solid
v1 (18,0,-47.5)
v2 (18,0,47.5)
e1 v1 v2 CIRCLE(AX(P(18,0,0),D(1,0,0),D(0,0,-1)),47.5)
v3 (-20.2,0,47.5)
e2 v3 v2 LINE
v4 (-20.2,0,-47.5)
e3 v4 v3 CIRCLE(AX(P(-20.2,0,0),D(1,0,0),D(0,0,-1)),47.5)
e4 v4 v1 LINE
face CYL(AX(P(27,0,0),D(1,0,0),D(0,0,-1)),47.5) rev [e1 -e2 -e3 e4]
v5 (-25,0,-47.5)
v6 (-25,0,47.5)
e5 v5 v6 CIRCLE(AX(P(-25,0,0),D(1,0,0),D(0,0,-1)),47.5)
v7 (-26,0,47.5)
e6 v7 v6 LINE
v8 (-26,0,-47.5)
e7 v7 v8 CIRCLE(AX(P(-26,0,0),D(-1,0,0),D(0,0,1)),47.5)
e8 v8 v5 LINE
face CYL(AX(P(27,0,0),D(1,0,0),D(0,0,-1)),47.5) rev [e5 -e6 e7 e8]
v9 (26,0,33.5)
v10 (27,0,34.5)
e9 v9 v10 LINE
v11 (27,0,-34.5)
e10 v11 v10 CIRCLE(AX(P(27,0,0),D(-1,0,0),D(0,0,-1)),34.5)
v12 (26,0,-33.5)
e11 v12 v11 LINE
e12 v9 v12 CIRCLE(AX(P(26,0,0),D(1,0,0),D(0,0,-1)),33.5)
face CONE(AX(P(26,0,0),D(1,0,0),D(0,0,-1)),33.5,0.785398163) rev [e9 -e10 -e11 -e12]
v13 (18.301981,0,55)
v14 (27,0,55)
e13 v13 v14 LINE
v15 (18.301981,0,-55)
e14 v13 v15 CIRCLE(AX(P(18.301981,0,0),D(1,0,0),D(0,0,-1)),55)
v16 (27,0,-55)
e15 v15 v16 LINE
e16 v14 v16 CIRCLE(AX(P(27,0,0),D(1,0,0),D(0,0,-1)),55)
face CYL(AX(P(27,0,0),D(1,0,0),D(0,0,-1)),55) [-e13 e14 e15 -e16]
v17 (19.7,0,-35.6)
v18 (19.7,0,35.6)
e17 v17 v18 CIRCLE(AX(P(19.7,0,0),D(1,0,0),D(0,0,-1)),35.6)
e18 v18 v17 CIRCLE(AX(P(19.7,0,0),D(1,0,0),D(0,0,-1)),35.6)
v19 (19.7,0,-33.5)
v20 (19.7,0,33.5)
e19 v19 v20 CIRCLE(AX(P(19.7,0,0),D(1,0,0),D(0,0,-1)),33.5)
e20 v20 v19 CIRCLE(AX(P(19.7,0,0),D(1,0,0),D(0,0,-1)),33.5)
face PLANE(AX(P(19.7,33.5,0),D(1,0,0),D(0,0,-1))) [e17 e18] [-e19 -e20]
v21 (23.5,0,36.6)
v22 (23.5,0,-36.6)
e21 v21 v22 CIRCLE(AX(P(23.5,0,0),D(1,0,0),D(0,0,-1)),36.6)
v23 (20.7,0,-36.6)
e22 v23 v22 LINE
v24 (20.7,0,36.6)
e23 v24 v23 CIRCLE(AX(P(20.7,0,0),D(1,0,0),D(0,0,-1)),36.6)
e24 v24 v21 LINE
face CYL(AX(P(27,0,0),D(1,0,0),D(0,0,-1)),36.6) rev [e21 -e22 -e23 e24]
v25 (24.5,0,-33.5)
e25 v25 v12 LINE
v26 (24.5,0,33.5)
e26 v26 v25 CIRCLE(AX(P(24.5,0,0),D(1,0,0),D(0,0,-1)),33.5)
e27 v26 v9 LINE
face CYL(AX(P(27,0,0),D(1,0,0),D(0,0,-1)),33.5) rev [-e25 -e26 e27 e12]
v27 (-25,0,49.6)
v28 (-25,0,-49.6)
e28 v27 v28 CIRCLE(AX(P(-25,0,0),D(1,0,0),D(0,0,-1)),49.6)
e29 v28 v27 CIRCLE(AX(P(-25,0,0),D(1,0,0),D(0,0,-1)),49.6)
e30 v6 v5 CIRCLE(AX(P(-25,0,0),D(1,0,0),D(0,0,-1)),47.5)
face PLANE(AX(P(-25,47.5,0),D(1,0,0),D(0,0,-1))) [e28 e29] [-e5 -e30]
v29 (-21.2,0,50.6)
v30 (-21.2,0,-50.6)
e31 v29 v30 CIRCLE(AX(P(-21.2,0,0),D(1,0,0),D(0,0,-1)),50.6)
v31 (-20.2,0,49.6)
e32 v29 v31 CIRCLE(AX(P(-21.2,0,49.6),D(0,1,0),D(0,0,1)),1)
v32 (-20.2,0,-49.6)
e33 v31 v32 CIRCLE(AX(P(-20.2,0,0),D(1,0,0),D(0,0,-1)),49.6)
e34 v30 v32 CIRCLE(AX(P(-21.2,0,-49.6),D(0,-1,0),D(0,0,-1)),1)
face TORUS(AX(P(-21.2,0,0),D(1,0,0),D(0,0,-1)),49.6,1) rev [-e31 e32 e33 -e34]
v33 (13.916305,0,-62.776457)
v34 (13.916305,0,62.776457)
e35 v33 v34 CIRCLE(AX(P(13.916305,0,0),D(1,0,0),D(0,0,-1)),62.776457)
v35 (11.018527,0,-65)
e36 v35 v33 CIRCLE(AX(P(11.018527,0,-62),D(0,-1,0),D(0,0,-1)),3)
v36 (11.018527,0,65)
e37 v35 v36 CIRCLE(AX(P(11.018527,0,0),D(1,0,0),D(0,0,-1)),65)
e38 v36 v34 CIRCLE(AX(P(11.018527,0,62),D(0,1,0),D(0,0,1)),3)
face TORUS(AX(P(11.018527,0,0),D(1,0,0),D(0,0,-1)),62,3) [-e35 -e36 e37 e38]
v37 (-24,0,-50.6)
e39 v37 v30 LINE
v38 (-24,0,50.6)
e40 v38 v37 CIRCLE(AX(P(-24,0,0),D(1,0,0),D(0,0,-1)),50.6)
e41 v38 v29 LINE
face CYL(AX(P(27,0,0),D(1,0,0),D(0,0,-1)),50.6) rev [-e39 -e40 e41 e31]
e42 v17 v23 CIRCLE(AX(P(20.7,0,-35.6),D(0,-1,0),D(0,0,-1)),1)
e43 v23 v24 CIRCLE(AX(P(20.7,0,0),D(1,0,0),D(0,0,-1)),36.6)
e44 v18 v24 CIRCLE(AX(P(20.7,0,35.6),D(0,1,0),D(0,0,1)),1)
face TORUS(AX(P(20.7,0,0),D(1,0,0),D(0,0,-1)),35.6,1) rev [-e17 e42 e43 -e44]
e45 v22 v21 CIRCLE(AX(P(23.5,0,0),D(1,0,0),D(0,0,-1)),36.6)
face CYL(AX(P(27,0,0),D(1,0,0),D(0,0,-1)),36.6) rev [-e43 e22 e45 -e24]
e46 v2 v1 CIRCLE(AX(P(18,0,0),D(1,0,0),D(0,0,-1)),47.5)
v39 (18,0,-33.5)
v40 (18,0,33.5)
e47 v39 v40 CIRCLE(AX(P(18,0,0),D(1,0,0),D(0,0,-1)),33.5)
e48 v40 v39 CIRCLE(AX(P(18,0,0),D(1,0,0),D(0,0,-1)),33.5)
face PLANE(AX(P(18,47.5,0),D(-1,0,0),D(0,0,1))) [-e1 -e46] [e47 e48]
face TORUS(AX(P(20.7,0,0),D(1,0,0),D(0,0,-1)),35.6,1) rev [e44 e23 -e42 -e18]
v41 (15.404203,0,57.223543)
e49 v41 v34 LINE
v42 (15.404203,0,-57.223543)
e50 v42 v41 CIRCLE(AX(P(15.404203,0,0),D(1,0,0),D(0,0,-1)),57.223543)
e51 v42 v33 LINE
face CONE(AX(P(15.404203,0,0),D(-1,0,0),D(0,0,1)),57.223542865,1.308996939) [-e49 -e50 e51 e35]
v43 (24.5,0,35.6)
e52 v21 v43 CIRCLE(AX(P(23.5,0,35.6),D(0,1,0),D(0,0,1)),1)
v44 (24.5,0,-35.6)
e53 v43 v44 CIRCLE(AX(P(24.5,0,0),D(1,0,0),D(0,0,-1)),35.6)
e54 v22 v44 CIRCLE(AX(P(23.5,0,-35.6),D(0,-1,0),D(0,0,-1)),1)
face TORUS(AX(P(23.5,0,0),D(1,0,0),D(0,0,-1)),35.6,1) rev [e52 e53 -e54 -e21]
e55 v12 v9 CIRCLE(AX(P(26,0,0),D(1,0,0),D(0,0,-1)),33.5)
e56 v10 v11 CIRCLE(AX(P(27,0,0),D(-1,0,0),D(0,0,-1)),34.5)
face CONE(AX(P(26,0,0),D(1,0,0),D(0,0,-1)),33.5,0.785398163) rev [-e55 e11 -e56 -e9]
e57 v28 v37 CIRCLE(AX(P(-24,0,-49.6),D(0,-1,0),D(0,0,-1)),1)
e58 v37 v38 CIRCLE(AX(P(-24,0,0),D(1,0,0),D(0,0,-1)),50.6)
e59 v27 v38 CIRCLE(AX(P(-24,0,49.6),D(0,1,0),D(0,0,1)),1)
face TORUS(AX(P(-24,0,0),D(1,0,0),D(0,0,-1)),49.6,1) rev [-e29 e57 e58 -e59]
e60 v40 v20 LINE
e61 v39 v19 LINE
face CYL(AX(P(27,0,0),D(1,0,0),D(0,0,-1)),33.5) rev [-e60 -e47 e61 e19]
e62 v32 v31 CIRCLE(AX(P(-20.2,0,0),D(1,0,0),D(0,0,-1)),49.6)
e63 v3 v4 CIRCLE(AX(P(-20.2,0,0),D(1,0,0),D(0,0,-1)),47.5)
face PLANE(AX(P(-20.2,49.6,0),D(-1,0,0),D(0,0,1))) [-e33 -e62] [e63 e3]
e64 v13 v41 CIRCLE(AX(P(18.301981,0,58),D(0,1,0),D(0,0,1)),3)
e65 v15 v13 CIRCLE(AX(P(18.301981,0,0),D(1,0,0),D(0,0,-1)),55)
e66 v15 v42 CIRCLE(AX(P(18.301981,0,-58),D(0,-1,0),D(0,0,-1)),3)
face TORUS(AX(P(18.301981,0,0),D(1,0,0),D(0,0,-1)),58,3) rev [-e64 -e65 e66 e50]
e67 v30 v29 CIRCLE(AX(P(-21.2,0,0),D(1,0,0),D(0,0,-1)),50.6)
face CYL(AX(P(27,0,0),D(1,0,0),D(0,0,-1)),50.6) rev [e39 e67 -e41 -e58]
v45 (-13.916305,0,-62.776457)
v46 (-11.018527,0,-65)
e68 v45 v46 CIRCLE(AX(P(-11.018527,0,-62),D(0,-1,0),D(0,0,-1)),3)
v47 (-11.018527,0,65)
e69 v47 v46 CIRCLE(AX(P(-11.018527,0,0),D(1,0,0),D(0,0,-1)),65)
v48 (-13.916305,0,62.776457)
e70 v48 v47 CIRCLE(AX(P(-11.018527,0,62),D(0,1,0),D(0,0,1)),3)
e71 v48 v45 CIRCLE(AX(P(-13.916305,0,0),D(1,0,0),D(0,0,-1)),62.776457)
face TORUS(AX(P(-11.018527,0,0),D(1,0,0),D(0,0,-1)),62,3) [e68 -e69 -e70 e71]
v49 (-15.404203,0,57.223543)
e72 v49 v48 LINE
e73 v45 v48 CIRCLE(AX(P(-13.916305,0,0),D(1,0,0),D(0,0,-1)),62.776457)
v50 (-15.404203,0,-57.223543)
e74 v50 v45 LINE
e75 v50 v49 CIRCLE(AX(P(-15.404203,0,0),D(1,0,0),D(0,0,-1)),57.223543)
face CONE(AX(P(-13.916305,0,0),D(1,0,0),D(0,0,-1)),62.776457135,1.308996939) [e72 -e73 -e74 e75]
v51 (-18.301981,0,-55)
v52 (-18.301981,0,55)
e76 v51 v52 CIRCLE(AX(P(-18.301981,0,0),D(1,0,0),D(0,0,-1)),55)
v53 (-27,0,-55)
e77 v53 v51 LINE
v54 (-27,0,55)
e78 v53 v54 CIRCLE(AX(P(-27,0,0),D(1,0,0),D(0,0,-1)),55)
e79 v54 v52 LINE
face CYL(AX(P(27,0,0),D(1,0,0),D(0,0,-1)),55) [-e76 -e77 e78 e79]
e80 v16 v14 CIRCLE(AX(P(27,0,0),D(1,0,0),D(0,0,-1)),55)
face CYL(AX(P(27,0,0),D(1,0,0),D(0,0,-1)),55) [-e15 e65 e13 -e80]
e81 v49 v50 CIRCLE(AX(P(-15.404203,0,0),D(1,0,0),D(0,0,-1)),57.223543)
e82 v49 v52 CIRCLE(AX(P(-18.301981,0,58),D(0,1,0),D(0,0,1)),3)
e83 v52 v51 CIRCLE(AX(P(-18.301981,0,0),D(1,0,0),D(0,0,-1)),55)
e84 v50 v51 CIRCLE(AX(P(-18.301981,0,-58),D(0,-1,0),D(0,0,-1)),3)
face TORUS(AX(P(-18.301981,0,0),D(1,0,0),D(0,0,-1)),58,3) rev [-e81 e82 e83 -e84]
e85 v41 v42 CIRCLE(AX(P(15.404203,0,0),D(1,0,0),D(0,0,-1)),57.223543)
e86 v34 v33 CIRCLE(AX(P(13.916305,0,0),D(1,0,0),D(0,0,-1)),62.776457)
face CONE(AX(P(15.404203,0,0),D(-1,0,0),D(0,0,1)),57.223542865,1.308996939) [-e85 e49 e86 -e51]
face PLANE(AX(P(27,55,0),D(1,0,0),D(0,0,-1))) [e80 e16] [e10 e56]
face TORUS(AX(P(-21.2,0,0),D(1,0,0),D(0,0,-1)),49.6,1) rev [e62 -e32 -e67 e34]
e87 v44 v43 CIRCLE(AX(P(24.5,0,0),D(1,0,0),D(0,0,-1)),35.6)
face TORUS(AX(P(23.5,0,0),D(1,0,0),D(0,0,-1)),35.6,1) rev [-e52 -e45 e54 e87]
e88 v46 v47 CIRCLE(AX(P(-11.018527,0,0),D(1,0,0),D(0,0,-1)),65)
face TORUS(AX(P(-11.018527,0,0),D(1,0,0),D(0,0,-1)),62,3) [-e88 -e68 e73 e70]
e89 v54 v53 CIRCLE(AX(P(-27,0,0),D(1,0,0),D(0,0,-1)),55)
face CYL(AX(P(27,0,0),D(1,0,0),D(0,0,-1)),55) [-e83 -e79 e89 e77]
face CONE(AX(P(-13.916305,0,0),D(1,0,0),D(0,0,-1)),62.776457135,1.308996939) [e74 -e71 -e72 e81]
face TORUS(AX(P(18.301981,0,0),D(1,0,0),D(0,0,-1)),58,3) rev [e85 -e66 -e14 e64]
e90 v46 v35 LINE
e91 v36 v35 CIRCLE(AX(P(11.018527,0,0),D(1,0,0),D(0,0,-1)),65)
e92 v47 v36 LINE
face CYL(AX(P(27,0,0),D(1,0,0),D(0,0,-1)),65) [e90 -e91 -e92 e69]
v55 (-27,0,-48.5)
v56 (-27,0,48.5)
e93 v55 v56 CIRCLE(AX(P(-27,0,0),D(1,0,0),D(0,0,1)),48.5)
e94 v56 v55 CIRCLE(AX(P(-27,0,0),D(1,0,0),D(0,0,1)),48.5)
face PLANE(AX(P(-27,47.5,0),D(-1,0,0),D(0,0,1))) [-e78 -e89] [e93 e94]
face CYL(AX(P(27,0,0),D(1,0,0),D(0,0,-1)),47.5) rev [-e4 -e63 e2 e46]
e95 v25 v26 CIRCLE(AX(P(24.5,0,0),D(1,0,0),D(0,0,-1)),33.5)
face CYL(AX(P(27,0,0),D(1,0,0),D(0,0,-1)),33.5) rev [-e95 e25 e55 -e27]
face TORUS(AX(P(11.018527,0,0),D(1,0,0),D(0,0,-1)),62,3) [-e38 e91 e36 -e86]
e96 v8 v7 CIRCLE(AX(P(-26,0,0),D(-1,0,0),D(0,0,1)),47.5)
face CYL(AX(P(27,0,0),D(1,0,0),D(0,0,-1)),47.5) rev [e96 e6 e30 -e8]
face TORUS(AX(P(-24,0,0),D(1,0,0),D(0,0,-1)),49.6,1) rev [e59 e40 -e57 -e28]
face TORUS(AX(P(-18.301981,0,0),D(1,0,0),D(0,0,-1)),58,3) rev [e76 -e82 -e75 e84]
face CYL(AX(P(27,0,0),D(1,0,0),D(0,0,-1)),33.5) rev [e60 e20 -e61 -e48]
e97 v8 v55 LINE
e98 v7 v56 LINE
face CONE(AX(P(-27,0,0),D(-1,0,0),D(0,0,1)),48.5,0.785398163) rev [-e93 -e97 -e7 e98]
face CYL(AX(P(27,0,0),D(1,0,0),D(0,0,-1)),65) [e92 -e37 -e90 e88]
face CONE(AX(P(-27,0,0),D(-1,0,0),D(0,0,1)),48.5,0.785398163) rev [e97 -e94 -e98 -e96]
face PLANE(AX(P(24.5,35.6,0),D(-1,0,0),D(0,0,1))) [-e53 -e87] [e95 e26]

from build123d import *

# Parameters (mm, degrees)
CHAMFER1_SIZE = 1


with BuildPart() as part:
    # Sketch1 → Revolve1 (revolve)
    with BuildSketch(Plane.XY, mode=Mode.PRIVATE) as revolve1_sk:
        with BuildLine():
            Line((-27, 47.5), (-27, 55))
            Line((-27, 55), (-18.301980964, 55))
            ThreePointArc((-18.301980964, 55), (-16.475696677, 55.619939979), (-15.404203485, 57.223542865))
            Line((-15.404203485, 57.223542865), (-13.916304591, 62.776457135))
            ThreePointArc((-13.916304591, 62.776457135), (-12.844811399, 64.380060021), (-11.018527112, 65))
            Line((-11.018527112, 65), (11.018527112, 65))
            ThreePointArc((11.018527112, 65), (12.844811399, 64.380060021), (13.916304591, 62.776457135))
            Line((13.916304591, 62.776457135), (15.404203485, 57.223542865))
            ThreePointArc((15.404203485, 57.223542865), (16.475696677, 55.619939979), (18.301980964, 55))
            Line((18.301980964, 55), (27, 55))
            Line((27, 55), (27, 33.5))
            Line((27, 33.5), (24.5, 33.5))
            Line((24.5, 33.5), (24.5, 35.6))
            ThreePointArc((24.5, 35.6), (24.207106781, 36.307106781), (23.5, 36.6))
            Line((23.5, 36.6), (20.7, 36.6))
            ThreePointArc((20.7, 36.6), (19.992893219, 36.307106781), (19.7, 35.6))
            Line((19.7, 35.6), (19.7, 33.5))
            Line((19.7, 33.5), (18, 33.5))
            Line((18, 33.5), (18, 47.5))
            Line((18, 47.5), (-20.2, 47.5))
            Line((-20.2, 47.5), (-20.2, 49.6))
            ThreePointArc((-20.2, 49.6), (-20.492893219, 50.307106781), (-21.2, 50.6))
            Line((-21.2, 50.6), (-24, 50.6))
            ThreePointArc((-24, 50.6), (-24.707106781, 50.307106781), (-25, 49.6))
            Line((-25, 49.6), (-25, 47.5))
            Line((-25, 47.5), (-27, 47.5))
        make_face()
    revolve(revolve1_sk.sketch.rotate(Axis((27, 0, 0), (-1, 0, 0)), 90), axis=Axis((27, 0, 0), (-1, 0, 0)))

    # Chamfer1
    chamfer1_edges = [part.edges().sort_by_distance(p)[0] for p in [
        (-27, 0, 47.5),
        (27, 0, 33.5),
    ]]
    chamfer(chamfer1_edges, length=CHAMFER1_SIZE)


solid = part.part
